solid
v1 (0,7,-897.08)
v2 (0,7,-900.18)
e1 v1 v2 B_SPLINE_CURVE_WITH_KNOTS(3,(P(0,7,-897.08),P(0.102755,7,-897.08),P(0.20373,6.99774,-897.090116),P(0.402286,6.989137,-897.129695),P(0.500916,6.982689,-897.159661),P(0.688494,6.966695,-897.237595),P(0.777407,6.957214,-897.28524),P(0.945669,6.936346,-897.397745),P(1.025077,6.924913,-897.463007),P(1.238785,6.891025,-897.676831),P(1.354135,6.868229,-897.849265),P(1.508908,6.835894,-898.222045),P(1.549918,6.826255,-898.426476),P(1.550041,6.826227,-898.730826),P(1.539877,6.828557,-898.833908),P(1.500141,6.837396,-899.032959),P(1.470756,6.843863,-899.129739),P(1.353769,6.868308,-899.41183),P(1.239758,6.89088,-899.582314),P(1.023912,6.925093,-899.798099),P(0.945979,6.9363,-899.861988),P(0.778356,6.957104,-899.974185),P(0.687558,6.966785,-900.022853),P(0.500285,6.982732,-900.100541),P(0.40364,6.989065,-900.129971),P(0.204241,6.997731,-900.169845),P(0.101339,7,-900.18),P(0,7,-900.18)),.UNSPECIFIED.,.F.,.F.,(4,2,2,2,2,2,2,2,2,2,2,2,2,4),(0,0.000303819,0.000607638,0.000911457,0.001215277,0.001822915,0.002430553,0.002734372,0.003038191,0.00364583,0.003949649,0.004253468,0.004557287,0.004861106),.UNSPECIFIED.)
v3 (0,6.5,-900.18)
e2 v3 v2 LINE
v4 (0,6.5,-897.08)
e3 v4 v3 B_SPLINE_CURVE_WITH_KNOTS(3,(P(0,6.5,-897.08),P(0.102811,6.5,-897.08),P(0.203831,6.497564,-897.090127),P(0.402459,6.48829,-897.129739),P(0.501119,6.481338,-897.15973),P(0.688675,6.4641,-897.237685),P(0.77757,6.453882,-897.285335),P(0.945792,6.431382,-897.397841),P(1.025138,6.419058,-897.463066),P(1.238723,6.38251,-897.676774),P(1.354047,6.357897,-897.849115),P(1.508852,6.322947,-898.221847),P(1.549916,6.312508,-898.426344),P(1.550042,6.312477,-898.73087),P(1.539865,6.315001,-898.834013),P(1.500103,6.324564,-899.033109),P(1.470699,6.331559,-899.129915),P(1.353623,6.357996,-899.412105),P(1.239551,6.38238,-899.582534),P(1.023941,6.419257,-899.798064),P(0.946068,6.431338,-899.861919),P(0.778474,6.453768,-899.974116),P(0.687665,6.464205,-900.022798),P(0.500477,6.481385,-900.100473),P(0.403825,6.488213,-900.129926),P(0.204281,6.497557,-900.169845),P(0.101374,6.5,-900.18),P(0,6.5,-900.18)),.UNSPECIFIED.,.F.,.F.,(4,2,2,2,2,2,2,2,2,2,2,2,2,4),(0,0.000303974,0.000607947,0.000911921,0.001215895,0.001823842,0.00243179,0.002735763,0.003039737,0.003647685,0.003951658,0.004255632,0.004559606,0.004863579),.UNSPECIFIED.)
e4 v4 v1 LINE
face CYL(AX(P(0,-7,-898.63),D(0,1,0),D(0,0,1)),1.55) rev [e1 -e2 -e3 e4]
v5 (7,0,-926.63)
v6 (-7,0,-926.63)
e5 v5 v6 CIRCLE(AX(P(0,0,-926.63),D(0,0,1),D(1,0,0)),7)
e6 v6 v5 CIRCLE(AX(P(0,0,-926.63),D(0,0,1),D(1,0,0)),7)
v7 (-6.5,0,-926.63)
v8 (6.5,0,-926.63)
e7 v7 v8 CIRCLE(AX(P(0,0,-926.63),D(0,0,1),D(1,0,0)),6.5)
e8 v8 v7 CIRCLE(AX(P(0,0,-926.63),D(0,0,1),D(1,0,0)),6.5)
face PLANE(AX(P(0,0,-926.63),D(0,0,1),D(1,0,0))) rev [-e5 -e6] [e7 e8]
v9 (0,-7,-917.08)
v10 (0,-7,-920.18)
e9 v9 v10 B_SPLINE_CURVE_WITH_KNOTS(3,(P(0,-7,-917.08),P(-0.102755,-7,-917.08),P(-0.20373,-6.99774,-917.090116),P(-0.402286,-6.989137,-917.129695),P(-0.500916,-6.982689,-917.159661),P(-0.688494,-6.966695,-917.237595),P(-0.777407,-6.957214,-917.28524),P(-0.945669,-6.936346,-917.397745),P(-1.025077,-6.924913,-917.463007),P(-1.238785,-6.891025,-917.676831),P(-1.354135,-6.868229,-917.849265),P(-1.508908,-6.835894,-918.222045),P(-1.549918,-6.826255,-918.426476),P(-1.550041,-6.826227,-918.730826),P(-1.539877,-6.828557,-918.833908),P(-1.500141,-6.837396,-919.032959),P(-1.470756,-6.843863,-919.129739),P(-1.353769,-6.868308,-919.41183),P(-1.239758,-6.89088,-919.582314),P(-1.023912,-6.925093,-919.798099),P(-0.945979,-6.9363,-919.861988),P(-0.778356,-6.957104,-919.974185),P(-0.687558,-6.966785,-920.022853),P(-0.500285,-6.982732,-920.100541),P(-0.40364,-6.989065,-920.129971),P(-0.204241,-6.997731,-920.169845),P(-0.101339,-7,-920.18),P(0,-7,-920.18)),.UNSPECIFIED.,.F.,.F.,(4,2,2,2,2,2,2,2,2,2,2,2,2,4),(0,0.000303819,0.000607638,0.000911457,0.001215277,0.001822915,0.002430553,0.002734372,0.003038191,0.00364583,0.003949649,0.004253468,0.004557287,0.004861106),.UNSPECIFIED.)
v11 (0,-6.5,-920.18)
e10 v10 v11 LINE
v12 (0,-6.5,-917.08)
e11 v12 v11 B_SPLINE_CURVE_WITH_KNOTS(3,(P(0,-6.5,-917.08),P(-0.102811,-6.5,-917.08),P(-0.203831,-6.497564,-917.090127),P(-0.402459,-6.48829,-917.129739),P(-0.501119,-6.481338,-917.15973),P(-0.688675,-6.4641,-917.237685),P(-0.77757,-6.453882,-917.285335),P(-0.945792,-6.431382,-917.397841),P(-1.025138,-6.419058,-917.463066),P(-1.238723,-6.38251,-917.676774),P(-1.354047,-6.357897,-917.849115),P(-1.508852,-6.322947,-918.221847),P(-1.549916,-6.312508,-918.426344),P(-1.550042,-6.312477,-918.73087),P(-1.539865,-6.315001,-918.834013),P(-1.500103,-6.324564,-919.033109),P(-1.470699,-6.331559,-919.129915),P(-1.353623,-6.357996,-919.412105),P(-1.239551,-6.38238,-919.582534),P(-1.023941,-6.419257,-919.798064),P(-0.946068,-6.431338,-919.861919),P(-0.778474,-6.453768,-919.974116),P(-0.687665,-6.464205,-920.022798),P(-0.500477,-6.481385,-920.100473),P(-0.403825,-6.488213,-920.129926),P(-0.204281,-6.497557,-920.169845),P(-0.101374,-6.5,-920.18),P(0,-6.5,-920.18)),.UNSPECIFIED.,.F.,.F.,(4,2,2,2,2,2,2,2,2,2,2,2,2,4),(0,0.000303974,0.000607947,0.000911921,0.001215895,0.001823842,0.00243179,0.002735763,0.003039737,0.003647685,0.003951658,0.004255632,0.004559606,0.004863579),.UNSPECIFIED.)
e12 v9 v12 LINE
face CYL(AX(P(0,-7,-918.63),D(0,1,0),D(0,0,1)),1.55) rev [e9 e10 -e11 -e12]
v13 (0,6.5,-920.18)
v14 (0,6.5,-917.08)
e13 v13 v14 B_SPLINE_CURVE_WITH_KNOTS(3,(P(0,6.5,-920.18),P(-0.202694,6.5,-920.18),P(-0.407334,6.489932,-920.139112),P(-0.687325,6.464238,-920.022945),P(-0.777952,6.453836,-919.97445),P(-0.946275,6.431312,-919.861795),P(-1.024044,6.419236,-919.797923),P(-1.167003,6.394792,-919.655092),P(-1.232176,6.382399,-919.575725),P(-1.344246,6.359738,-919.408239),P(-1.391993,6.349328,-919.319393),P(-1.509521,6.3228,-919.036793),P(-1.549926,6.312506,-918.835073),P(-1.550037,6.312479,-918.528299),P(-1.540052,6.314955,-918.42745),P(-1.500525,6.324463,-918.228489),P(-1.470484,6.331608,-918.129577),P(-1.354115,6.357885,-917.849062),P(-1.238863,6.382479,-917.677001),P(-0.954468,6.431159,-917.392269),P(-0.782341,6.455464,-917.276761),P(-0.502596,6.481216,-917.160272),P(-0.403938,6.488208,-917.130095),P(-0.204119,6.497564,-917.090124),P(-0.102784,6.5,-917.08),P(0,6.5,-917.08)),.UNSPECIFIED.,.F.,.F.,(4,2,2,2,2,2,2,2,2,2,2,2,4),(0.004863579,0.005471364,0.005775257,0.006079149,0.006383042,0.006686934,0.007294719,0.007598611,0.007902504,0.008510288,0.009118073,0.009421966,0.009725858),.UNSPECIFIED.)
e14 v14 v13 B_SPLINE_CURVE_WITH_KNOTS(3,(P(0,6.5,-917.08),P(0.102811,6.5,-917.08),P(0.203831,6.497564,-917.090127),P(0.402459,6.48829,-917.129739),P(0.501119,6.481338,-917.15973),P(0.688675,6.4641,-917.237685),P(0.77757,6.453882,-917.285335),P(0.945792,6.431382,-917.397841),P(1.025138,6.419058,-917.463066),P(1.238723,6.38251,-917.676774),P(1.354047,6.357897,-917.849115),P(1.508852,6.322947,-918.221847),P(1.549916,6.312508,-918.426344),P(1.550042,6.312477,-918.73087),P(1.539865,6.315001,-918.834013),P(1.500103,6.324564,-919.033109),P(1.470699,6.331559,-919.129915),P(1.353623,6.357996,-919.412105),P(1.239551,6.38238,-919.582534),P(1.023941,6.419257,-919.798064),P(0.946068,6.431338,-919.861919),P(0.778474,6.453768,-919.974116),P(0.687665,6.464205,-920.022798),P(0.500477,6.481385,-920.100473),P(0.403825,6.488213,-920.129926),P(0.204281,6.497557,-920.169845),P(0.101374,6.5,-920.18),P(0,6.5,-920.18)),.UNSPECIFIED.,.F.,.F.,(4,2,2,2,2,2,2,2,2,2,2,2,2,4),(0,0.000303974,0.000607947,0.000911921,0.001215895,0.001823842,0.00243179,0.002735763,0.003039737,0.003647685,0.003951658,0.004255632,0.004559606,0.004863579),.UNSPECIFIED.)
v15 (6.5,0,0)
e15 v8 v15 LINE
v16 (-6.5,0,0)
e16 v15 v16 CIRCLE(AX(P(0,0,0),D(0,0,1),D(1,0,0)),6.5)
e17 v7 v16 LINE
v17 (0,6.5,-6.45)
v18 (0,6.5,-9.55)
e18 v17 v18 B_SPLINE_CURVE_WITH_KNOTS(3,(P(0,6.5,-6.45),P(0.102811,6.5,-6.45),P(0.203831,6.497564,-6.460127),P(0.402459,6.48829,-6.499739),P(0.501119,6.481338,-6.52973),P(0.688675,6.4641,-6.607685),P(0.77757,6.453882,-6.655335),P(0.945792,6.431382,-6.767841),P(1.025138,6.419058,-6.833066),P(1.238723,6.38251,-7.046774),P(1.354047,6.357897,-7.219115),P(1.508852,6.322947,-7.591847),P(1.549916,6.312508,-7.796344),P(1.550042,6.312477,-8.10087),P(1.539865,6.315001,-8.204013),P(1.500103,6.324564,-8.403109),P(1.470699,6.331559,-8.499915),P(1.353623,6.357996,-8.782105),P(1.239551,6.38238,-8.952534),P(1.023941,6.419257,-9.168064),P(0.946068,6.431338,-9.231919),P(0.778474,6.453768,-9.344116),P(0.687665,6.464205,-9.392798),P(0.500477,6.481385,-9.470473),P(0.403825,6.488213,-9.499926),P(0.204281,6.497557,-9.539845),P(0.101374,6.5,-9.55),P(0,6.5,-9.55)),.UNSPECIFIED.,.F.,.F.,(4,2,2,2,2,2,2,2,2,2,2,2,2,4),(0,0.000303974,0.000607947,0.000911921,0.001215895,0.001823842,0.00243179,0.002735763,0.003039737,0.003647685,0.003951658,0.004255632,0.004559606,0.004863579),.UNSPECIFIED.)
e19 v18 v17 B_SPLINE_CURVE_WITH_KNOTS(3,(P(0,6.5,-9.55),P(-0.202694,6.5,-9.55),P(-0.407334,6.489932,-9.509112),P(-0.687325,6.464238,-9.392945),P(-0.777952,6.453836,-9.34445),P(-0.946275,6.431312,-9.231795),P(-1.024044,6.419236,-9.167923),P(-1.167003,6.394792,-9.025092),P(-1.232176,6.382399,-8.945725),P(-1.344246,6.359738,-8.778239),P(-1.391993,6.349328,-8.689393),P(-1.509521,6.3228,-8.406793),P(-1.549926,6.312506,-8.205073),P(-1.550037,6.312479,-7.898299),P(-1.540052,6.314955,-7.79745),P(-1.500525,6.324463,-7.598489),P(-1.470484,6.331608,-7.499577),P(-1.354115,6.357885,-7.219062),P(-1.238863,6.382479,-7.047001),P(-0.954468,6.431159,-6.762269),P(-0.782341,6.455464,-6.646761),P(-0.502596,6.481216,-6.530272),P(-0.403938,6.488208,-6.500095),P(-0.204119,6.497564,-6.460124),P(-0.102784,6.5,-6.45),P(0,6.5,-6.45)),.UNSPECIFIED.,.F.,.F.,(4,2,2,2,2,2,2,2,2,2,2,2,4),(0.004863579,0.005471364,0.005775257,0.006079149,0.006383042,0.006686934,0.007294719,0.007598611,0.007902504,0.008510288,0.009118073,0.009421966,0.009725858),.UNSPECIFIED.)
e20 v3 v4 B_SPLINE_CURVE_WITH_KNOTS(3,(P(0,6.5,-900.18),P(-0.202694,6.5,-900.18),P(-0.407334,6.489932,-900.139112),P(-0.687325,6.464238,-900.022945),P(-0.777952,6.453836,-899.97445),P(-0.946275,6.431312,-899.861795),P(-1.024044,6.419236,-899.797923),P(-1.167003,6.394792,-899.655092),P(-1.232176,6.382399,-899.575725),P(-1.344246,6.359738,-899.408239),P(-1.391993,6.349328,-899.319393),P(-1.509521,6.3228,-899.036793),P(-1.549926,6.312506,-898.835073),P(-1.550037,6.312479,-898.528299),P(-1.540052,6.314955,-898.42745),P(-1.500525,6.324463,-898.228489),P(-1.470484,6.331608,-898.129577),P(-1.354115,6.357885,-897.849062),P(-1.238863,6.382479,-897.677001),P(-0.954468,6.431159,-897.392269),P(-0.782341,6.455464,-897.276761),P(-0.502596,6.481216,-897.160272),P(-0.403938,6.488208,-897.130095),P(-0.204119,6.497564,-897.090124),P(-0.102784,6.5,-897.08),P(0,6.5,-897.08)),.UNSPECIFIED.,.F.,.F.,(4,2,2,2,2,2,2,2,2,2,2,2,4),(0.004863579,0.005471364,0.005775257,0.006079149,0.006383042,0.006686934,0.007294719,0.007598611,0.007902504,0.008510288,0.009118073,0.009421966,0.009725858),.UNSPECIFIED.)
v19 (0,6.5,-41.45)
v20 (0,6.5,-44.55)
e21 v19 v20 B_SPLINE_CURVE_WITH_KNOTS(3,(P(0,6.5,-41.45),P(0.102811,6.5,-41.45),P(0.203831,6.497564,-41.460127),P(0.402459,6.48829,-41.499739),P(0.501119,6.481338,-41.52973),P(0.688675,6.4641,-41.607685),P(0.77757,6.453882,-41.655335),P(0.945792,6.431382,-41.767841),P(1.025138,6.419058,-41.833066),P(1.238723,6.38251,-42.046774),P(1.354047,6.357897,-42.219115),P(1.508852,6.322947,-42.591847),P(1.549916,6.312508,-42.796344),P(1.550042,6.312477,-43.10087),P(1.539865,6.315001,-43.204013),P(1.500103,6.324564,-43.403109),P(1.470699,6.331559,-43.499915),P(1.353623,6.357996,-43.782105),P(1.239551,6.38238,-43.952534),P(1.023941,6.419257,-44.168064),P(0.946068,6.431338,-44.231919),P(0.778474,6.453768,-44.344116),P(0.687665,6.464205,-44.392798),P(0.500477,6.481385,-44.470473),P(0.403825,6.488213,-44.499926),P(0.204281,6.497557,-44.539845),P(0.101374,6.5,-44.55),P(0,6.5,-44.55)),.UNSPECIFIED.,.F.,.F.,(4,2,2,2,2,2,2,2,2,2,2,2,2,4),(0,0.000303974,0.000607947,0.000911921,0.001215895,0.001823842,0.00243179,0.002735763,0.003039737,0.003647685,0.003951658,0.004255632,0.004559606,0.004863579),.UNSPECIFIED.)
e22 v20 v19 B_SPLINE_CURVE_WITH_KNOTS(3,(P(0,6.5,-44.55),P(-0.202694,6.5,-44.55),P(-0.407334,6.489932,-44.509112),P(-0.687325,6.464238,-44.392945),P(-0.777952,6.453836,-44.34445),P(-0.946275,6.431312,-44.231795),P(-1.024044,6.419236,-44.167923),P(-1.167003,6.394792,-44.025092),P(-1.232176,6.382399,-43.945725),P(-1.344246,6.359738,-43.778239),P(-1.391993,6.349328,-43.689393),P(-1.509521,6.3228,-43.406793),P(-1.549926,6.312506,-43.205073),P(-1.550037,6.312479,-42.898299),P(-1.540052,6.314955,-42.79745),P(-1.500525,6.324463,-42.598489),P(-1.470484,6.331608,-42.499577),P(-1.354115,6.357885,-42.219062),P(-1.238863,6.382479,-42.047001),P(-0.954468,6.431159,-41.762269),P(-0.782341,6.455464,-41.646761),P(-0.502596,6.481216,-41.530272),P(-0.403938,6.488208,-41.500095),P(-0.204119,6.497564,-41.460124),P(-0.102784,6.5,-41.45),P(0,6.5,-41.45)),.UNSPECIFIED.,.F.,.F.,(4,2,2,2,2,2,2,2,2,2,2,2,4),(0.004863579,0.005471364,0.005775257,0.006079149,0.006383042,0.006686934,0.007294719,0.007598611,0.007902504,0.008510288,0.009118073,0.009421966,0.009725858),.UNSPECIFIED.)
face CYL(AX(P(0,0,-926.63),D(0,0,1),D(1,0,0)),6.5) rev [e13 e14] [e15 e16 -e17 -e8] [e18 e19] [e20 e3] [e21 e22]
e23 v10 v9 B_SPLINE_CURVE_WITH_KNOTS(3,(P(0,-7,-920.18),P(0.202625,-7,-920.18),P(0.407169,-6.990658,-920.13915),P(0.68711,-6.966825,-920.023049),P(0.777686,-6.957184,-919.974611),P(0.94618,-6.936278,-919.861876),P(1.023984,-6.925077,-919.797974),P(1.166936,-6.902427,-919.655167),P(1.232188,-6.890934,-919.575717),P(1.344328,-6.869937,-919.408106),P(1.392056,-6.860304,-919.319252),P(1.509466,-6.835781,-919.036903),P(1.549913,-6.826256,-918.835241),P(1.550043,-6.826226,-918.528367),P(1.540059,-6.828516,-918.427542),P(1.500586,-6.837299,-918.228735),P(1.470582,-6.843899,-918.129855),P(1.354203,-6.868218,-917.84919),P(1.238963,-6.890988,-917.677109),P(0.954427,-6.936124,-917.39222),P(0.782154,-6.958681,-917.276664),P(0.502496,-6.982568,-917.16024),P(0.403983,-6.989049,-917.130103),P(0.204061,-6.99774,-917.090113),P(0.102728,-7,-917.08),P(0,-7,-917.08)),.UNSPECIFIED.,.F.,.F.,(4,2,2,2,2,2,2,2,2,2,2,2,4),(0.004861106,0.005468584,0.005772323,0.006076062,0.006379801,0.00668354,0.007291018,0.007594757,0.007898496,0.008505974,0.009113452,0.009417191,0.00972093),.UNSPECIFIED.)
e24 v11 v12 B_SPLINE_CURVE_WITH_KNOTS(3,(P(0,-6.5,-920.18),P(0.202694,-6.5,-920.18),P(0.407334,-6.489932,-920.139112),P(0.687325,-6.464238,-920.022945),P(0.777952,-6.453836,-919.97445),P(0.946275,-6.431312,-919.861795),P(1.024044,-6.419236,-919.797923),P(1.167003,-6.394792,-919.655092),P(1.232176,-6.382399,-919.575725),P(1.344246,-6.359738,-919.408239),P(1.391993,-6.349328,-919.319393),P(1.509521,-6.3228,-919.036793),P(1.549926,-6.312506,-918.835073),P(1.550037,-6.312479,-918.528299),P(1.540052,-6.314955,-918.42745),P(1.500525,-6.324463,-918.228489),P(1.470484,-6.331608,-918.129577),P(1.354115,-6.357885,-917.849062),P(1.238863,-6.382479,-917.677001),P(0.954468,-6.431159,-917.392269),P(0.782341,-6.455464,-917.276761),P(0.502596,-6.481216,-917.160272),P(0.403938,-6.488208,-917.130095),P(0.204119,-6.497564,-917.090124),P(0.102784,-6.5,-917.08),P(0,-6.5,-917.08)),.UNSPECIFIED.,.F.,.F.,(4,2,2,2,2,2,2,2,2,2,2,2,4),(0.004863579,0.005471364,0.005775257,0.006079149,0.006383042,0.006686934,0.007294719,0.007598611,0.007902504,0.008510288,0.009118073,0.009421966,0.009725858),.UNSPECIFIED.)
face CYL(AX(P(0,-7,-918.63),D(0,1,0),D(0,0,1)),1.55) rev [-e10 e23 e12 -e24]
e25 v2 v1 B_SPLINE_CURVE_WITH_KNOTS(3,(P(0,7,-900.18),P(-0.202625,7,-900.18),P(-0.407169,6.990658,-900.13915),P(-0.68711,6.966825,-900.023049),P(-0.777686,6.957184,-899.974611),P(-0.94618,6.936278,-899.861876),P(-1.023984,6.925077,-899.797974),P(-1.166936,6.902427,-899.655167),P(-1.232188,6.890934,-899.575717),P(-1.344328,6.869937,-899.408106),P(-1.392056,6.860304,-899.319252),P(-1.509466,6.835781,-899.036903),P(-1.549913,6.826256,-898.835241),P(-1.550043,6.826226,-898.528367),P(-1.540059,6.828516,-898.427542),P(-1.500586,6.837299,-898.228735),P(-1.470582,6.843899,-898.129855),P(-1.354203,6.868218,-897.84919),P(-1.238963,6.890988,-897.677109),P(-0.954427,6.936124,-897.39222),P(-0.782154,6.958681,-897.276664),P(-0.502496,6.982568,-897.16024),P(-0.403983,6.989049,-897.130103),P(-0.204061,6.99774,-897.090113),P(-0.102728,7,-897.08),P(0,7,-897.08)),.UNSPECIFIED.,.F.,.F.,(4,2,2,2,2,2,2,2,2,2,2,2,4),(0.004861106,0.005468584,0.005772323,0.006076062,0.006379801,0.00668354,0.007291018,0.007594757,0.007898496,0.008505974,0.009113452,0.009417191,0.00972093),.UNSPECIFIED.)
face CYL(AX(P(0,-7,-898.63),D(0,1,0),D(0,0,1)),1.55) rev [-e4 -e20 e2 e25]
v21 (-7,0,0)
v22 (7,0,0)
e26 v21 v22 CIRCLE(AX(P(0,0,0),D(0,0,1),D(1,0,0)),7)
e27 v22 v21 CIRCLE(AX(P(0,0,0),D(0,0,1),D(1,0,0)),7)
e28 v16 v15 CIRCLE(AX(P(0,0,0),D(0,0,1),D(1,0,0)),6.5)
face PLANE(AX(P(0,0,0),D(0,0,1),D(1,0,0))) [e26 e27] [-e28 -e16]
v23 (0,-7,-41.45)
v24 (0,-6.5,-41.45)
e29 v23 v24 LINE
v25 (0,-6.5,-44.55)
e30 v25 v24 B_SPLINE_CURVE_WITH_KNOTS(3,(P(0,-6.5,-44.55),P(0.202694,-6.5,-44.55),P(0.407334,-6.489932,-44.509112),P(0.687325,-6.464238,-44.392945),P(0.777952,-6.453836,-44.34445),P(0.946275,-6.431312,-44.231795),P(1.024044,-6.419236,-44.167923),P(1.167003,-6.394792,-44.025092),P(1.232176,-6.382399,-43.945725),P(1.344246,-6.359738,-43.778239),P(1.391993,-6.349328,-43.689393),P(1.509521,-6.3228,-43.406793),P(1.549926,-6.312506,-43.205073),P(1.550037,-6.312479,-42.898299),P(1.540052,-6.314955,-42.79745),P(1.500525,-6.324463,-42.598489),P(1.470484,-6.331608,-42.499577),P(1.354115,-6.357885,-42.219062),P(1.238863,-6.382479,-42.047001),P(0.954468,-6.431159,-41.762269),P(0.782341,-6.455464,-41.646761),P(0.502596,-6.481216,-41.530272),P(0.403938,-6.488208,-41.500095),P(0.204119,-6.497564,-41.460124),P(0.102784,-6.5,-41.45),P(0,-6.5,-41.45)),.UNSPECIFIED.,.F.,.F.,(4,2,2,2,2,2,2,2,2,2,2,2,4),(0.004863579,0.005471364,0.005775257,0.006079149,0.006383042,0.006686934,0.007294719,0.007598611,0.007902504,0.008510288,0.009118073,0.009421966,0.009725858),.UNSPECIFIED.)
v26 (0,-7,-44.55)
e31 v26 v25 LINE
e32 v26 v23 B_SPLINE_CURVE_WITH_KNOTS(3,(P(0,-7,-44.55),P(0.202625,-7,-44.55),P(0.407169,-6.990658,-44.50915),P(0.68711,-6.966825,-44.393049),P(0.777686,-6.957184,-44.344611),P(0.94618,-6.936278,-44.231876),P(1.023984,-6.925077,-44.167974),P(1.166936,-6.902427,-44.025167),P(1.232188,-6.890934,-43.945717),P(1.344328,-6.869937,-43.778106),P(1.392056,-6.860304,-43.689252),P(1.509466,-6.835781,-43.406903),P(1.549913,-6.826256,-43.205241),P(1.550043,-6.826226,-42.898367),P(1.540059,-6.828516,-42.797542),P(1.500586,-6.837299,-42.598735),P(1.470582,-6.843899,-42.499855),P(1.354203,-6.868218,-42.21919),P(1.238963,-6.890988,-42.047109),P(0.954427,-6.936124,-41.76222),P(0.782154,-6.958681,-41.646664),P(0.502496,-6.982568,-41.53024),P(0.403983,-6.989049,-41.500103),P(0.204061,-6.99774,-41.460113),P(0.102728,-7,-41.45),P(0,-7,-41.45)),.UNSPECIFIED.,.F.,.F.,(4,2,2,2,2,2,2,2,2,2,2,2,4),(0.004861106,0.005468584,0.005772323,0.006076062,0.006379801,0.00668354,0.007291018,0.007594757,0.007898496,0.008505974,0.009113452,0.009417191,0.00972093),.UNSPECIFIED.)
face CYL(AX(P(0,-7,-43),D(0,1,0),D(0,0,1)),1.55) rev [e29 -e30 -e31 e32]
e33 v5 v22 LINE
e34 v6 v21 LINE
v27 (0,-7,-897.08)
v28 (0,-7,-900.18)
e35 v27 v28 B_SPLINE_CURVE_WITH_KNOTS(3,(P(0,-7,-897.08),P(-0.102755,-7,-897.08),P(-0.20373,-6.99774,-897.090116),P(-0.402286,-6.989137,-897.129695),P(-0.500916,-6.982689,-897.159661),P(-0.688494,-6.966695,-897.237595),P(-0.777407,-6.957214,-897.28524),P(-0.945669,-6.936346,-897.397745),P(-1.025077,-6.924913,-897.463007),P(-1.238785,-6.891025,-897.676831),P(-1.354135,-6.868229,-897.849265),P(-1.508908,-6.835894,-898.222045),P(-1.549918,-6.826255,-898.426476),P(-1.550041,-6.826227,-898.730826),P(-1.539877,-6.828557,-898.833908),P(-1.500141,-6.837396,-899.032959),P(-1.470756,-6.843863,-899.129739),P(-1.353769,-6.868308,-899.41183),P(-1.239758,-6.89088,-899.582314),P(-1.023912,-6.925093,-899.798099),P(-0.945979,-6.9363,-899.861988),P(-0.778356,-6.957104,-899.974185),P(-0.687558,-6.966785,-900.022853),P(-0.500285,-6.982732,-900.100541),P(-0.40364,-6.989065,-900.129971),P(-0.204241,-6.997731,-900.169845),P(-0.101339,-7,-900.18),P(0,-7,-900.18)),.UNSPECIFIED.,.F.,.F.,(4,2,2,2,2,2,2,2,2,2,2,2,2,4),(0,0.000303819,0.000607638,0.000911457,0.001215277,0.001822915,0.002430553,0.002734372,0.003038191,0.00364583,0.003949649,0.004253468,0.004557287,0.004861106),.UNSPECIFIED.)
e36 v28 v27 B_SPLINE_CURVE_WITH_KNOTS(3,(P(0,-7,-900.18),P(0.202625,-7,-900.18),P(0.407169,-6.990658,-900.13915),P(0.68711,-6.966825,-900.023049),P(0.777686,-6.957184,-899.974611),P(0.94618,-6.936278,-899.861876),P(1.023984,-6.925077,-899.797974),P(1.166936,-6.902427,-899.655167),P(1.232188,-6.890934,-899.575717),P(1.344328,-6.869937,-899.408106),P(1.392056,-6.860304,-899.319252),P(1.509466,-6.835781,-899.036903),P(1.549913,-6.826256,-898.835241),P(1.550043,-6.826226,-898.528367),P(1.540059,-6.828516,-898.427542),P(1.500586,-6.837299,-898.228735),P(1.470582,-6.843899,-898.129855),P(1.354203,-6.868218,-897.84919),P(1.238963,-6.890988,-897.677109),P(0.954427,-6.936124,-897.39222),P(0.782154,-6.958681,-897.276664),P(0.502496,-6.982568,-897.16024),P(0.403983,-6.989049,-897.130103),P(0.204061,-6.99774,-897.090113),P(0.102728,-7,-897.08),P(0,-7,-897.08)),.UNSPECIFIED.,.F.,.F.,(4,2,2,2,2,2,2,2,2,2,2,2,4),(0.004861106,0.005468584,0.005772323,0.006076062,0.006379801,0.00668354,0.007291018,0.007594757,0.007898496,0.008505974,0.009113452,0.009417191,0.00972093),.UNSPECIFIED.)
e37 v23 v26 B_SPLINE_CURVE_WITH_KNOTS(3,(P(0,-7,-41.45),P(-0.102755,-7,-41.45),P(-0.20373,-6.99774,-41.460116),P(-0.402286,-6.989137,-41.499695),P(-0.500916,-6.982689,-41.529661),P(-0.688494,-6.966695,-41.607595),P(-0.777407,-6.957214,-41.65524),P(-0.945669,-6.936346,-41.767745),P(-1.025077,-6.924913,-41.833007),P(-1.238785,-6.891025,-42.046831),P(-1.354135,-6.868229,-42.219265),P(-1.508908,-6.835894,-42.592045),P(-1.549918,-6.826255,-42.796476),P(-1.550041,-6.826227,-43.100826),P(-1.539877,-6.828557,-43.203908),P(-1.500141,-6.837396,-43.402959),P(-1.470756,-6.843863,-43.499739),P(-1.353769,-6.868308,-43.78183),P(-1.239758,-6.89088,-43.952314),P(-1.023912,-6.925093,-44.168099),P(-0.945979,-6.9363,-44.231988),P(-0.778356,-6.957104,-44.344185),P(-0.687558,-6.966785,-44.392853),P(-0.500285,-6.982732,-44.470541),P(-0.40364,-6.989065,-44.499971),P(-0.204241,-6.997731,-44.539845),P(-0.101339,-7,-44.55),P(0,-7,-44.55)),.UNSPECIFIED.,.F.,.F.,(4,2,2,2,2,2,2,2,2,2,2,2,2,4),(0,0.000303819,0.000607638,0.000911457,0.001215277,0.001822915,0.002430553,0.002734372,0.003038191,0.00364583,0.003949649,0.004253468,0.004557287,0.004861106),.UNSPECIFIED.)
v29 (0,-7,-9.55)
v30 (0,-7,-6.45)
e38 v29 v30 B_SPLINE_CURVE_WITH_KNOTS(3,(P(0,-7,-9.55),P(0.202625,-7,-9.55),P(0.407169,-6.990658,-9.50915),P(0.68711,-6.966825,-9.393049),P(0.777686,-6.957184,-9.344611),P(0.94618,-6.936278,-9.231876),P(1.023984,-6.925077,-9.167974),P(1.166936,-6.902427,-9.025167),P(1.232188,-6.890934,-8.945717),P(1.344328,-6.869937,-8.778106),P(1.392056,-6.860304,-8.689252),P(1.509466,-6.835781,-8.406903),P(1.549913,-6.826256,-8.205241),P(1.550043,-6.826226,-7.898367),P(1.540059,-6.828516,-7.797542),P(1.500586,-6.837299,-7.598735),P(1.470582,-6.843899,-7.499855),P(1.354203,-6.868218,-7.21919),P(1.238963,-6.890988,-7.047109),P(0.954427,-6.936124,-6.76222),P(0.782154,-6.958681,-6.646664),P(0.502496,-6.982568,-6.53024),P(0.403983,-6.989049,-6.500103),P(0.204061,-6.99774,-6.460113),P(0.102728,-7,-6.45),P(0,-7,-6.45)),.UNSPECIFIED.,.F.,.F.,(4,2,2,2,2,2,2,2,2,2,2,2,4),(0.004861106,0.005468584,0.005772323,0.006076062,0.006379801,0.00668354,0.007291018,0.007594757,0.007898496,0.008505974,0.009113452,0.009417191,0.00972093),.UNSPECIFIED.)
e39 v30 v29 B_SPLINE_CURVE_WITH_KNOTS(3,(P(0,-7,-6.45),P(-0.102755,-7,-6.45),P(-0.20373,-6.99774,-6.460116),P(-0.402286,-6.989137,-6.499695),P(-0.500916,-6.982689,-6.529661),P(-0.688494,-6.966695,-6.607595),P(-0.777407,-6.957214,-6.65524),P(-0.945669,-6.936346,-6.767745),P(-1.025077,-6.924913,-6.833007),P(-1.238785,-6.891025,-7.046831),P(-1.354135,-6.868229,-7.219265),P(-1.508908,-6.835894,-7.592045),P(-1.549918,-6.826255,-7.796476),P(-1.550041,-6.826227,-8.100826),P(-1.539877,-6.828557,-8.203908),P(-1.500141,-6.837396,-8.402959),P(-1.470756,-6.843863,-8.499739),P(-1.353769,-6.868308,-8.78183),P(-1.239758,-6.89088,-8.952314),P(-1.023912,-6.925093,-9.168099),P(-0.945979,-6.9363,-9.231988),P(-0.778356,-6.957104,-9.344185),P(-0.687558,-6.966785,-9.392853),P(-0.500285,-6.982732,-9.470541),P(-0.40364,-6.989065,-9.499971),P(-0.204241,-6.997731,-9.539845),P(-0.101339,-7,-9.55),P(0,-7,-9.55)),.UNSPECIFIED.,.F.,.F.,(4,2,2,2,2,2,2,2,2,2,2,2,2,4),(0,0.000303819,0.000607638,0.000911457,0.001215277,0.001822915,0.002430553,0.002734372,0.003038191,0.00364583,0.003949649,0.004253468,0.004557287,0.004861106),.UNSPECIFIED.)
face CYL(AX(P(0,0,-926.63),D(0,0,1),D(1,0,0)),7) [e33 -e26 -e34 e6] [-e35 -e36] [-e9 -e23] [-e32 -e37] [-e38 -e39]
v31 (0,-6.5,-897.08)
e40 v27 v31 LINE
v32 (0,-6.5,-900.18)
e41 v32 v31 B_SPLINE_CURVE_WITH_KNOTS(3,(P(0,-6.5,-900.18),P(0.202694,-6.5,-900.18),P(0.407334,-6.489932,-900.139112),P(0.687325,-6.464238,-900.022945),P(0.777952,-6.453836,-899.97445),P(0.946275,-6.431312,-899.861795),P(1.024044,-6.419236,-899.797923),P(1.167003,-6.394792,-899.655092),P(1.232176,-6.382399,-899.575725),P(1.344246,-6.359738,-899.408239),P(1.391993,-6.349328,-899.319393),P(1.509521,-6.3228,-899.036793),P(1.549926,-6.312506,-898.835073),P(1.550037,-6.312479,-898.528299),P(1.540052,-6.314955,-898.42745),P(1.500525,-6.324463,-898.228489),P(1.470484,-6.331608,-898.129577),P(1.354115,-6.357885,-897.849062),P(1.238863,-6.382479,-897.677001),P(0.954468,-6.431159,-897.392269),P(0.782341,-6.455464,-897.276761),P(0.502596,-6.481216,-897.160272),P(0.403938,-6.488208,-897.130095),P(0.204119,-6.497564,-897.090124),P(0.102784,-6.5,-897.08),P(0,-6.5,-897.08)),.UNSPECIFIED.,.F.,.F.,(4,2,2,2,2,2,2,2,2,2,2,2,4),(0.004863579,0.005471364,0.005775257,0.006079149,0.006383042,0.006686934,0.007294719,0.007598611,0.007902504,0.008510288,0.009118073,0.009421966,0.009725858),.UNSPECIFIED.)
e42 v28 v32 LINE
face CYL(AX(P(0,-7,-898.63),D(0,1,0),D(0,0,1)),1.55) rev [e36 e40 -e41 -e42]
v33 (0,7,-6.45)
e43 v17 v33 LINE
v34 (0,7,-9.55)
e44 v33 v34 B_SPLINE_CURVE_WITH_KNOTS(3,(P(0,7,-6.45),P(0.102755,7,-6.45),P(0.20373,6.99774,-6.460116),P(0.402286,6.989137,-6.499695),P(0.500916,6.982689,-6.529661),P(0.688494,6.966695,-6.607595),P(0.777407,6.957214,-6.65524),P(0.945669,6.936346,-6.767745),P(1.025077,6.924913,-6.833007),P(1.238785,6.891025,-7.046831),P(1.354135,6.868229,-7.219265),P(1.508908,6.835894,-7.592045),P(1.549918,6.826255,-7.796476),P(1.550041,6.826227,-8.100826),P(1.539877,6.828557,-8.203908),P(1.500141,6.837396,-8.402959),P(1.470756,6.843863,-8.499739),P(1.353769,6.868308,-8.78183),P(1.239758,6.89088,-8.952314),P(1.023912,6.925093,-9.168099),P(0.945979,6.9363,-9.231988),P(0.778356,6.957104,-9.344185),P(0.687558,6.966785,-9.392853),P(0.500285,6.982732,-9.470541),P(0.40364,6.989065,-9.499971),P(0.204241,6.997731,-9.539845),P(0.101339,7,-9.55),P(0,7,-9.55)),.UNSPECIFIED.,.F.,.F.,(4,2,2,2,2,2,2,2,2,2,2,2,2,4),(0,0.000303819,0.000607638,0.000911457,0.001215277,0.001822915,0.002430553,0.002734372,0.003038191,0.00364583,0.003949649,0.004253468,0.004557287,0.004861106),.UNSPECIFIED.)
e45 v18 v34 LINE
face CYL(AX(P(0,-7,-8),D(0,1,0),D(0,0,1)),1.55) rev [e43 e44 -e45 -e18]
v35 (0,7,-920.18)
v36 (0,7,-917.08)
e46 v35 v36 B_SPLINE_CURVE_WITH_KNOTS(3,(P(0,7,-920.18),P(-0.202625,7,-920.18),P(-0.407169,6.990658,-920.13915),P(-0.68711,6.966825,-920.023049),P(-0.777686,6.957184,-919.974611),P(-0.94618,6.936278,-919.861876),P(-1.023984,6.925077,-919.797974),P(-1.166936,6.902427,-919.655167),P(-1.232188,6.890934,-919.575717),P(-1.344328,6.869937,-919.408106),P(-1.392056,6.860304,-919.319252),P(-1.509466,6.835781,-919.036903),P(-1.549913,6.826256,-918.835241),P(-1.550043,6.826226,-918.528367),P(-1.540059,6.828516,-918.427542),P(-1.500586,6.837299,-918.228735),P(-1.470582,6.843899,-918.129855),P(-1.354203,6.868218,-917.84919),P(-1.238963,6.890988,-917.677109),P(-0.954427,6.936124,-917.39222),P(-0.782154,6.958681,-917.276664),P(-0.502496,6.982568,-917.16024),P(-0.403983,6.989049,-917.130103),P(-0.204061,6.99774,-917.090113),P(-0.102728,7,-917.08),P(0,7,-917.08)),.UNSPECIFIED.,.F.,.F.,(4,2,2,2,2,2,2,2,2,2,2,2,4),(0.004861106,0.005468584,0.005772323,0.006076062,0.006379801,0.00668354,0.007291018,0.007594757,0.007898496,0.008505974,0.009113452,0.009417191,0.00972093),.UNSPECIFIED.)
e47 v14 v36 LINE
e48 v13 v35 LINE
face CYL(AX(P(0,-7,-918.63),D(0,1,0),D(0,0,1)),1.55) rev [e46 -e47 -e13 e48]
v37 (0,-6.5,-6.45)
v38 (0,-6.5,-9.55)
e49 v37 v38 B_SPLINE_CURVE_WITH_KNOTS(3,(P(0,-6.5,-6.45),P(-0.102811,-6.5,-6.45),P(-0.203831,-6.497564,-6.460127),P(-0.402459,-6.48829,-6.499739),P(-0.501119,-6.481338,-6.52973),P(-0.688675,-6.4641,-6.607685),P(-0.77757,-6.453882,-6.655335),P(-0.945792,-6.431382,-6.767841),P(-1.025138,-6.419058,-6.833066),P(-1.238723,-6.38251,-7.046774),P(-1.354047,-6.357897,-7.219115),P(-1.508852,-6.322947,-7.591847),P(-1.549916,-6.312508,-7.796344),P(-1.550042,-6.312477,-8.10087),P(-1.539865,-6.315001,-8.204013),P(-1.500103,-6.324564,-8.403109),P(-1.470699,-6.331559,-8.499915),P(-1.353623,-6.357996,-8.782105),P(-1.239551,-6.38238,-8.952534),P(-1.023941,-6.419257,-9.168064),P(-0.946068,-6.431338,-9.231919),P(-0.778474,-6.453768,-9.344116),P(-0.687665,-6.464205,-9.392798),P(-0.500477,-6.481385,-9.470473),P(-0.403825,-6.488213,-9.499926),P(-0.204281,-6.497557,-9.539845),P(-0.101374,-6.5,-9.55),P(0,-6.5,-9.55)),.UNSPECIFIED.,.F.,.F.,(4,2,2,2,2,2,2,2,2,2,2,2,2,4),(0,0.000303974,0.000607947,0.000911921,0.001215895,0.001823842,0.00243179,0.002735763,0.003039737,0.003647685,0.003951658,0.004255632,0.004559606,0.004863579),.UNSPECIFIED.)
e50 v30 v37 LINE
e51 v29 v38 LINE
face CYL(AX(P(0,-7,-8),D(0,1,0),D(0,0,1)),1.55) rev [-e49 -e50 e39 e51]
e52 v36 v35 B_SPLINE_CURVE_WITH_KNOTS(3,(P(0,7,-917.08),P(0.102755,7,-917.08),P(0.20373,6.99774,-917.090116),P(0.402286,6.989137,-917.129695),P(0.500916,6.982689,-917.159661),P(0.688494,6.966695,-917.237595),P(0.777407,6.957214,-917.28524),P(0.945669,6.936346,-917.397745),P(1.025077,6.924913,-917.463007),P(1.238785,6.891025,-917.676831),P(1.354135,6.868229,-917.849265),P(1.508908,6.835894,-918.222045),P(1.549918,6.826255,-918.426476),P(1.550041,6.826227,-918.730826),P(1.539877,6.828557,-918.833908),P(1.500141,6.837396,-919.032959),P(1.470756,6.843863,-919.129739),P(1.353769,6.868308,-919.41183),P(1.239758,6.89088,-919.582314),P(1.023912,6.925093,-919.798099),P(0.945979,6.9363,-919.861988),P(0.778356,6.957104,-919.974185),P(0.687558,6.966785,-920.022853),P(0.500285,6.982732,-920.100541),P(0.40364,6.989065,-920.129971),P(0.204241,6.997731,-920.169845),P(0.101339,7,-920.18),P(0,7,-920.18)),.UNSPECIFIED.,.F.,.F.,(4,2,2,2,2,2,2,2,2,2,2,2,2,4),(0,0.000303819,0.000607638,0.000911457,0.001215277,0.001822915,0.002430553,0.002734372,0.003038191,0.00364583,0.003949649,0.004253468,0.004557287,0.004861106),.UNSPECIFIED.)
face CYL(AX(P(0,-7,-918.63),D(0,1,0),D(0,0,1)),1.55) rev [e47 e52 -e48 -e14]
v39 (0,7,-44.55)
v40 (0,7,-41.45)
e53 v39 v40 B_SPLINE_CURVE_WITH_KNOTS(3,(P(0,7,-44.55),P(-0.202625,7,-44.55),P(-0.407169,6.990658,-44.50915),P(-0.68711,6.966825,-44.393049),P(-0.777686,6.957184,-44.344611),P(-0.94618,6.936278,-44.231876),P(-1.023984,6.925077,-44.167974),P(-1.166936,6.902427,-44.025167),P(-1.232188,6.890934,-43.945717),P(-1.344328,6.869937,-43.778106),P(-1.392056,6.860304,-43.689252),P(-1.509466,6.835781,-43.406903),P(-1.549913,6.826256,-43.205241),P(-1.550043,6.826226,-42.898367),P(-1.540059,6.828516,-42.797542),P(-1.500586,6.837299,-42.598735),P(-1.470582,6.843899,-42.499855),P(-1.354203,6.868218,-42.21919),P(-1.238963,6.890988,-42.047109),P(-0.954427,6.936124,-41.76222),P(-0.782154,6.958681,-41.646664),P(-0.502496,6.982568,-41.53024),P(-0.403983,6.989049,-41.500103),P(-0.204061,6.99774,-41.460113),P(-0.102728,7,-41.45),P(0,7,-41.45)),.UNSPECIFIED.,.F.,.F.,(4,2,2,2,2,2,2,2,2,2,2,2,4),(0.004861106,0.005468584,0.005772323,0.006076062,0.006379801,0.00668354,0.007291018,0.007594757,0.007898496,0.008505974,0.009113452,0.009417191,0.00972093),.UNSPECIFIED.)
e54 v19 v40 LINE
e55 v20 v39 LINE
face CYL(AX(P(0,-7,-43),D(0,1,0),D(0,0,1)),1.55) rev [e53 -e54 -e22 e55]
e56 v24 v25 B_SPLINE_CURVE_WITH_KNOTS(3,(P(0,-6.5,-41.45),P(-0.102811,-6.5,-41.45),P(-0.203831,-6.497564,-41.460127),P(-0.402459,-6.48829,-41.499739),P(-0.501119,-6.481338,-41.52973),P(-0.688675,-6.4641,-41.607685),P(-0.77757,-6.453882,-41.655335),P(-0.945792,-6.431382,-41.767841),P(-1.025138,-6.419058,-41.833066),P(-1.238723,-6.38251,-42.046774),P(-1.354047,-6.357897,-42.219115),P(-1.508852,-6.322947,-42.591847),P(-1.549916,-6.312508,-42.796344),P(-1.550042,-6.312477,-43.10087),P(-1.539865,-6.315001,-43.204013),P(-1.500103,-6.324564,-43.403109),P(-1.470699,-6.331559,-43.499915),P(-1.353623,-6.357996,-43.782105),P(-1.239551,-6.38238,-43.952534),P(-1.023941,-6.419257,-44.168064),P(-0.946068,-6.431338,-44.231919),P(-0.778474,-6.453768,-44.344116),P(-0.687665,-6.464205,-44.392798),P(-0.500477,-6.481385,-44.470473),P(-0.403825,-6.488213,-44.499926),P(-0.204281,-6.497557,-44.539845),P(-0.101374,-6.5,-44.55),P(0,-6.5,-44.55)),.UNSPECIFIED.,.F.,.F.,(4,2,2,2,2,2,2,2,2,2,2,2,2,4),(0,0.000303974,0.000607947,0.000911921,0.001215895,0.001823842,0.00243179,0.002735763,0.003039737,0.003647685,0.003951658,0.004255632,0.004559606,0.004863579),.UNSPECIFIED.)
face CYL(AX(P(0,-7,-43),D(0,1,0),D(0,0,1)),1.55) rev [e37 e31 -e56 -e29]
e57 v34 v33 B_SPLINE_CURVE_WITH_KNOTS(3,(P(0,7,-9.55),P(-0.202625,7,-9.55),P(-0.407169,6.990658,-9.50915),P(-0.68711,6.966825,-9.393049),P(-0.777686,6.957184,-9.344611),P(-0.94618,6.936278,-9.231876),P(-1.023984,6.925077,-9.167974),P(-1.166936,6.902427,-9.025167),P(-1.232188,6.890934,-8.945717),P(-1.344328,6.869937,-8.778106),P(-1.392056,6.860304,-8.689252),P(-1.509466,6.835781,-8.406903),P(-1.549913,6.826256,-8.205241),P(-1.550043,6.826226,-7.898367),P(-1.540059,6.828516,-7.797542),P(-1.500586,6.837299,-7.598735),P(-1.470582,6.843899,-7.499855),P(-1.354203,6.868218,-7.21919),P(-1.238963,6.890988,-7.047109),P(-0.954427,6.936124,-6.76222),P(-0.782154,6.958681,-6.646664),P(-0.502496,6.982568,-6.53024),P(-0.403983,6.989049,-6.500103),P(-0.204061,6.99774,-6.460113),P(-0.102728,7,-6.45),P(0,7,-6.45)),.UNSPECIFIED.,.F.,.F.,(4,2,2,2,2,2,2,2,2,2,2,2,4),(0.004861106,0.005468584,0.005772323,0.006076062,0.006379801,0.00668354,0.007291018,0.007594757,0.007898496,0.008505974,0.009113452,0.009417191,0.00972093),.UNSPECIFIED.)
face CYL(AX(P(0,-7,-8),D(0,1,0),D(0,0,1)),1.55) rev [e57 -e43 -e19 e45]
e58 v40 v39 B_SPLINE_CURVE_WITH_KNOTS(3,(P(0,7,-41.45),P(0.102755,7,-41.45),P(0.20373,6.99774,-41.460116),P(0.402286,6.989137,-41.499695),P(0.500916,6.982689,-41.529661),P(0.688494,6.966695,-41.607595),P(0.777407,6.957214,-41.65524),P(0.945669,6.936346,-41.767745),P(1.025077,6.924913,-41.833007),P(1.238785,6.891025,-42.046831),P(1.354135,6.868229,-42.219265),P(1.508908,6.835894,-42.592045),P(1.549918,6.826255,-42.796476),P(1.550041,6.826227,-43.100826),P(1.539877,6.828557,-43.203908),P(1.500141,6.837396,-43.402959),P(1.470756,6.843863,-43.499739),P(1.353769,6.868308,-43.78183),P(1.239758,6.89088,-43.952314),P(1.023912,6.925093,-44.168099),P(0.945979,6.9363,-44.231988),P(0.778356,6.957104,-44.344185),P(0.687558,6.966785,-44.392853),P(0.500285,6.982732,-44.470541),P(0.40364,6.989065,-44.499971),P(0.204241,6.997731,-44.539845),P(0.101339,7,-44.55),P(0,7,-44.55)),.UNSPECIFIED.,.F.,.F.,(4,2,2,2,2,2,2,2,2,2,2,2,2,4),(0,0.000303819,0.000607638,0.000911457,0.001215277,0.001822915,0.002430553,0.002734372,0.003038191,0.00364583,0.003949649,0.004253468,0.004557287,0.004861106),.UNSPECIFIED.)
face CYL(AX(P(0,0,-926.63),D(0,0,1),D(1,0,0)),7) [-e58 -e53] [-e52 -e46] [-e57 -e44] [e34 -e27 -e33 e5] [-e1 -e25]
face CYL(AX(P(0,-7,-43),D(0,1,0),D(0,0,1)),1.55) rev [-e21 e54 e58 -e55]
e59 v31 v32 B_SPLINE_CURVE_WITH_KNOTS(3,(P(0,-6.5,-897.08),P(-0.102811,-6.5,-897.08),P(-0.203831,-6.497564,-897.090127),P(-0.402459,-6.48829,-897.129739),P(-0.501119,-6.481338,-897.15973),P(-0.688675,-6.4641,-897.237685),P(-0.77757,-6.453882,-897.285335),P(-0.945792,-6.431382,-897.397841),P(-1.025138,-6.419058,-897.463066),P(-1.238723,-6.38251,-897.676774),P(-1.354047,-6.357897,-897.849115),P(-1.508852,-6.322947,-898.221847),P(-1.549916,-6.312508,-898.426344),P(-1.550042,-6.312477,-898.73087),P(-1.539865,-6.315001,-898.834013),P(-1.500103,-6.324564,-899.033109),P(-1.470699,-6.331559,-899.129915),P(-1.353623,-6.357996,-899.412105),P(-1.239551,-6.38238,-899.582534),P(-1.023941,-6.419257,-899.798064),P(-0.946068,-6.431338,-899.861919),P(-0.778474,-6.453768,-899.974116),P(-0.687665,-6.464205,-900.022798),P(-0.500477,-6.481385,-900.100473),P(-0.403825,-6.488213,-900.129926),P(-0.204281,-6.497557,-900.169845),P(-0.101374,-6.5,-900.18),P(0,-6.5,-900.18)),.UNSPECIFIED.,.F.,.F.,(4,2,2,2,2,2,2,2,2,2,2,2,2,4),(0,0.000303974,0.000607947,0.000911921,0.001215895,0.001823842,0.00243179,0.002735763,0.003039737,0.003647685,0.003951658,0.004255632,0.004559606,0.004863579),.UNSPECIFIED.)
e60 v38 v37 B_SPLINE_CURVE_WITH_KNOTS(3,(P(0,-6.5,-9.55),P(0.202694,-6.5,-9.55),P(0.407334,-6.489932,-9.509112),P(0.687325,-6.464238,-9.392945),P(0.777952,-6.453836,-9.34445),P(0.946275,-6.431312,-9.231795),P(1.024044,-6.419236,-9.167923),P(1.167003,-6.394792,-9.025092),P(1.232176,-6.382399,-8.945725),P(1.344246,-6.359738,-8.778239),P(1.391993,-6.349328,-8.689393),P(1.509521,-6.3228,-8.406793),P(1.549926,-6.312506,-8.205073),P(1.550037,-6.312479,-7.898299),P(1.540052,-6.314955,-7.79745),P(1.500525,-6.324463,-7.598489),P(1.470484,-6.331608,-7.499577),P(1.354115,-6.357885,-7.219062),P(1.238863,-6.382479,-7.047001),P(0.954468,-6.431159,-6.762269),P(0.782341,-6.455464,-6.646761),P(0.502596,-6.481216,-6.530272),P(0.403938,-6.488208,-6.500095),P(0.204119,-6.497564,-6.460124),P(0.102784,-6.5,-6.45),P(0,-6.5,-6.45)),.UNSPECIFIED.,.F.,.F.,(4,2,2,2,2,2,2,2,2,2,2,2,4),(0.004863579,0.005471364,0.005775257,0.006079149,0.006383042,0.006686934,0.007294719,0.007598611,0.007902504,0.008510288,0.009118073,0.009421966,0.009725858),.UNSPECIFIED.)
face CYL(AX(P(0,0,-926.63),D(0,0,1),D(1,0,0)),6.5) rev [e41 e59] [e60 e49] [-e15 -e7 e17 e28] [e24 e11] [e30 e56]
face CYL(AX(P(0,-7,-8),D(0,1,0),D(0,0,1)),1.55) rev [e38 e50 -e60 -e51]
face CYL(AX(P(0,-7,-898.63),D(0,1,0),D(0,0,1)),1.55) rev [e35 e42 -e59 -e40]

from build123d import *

# Parameters (mm, degrees)
SKETCH_1_R               = 7
SKETCH_1_R_2             = 6.5
EXTRUDE_1_DEPTH          = 926.63
CUT_EXTRUDE_1_DEPTH      = 927.682878281
CUT_EXTRUDE_1_DEPTH_BACK = 927.682878281
SKETCH_2_R               = 1.55


with BuildPart() as part:
    # 草图1 → 凸台-拉伸1 (new body)
    with BuildSketch(Plane.XY):
        Circle(SKETCH_1_R)
        Circle(SKETCH_1_R_2, mode=Mode.SUBTRACT)
    extrude(amount=-EXTRUDE_1_DEPTH)

    # 草图2 → 切除-拉伸1 (cut, two sides: drawn at the far end of the back side and taken through both)
    with BuildSketch(Plane(origin=(0, 0, 0), x_dir=(1, 0, 0), z_dir=(0, 1, 0)).offset(-CUT_EXTRUDE_1_DEPTH_BACK)):
        with Locations(Location((0, 8, 0), (0, 0, 270))):
            Circle(SKETCH_2_R)
        with Locations(Location((0, 43, 0), (0, 0, 270))):
            Circle(SKETCH_2_R)
        with Locations(Location((0, 918.63, 0), (0, 0, 270))):
            Circle(SKETCH_2_R)
        with Locations(Location((0, 898.63, 0), (0, 0, 270))):
            Circle(SKETCH_2_R)
    extrude(amount=CUT_EXTRUDE_1_DEPTH + CUT_EXTRUDE_1_DEPTH_BACK, mode=Mode.SUBTRACT)


solid = part.part
